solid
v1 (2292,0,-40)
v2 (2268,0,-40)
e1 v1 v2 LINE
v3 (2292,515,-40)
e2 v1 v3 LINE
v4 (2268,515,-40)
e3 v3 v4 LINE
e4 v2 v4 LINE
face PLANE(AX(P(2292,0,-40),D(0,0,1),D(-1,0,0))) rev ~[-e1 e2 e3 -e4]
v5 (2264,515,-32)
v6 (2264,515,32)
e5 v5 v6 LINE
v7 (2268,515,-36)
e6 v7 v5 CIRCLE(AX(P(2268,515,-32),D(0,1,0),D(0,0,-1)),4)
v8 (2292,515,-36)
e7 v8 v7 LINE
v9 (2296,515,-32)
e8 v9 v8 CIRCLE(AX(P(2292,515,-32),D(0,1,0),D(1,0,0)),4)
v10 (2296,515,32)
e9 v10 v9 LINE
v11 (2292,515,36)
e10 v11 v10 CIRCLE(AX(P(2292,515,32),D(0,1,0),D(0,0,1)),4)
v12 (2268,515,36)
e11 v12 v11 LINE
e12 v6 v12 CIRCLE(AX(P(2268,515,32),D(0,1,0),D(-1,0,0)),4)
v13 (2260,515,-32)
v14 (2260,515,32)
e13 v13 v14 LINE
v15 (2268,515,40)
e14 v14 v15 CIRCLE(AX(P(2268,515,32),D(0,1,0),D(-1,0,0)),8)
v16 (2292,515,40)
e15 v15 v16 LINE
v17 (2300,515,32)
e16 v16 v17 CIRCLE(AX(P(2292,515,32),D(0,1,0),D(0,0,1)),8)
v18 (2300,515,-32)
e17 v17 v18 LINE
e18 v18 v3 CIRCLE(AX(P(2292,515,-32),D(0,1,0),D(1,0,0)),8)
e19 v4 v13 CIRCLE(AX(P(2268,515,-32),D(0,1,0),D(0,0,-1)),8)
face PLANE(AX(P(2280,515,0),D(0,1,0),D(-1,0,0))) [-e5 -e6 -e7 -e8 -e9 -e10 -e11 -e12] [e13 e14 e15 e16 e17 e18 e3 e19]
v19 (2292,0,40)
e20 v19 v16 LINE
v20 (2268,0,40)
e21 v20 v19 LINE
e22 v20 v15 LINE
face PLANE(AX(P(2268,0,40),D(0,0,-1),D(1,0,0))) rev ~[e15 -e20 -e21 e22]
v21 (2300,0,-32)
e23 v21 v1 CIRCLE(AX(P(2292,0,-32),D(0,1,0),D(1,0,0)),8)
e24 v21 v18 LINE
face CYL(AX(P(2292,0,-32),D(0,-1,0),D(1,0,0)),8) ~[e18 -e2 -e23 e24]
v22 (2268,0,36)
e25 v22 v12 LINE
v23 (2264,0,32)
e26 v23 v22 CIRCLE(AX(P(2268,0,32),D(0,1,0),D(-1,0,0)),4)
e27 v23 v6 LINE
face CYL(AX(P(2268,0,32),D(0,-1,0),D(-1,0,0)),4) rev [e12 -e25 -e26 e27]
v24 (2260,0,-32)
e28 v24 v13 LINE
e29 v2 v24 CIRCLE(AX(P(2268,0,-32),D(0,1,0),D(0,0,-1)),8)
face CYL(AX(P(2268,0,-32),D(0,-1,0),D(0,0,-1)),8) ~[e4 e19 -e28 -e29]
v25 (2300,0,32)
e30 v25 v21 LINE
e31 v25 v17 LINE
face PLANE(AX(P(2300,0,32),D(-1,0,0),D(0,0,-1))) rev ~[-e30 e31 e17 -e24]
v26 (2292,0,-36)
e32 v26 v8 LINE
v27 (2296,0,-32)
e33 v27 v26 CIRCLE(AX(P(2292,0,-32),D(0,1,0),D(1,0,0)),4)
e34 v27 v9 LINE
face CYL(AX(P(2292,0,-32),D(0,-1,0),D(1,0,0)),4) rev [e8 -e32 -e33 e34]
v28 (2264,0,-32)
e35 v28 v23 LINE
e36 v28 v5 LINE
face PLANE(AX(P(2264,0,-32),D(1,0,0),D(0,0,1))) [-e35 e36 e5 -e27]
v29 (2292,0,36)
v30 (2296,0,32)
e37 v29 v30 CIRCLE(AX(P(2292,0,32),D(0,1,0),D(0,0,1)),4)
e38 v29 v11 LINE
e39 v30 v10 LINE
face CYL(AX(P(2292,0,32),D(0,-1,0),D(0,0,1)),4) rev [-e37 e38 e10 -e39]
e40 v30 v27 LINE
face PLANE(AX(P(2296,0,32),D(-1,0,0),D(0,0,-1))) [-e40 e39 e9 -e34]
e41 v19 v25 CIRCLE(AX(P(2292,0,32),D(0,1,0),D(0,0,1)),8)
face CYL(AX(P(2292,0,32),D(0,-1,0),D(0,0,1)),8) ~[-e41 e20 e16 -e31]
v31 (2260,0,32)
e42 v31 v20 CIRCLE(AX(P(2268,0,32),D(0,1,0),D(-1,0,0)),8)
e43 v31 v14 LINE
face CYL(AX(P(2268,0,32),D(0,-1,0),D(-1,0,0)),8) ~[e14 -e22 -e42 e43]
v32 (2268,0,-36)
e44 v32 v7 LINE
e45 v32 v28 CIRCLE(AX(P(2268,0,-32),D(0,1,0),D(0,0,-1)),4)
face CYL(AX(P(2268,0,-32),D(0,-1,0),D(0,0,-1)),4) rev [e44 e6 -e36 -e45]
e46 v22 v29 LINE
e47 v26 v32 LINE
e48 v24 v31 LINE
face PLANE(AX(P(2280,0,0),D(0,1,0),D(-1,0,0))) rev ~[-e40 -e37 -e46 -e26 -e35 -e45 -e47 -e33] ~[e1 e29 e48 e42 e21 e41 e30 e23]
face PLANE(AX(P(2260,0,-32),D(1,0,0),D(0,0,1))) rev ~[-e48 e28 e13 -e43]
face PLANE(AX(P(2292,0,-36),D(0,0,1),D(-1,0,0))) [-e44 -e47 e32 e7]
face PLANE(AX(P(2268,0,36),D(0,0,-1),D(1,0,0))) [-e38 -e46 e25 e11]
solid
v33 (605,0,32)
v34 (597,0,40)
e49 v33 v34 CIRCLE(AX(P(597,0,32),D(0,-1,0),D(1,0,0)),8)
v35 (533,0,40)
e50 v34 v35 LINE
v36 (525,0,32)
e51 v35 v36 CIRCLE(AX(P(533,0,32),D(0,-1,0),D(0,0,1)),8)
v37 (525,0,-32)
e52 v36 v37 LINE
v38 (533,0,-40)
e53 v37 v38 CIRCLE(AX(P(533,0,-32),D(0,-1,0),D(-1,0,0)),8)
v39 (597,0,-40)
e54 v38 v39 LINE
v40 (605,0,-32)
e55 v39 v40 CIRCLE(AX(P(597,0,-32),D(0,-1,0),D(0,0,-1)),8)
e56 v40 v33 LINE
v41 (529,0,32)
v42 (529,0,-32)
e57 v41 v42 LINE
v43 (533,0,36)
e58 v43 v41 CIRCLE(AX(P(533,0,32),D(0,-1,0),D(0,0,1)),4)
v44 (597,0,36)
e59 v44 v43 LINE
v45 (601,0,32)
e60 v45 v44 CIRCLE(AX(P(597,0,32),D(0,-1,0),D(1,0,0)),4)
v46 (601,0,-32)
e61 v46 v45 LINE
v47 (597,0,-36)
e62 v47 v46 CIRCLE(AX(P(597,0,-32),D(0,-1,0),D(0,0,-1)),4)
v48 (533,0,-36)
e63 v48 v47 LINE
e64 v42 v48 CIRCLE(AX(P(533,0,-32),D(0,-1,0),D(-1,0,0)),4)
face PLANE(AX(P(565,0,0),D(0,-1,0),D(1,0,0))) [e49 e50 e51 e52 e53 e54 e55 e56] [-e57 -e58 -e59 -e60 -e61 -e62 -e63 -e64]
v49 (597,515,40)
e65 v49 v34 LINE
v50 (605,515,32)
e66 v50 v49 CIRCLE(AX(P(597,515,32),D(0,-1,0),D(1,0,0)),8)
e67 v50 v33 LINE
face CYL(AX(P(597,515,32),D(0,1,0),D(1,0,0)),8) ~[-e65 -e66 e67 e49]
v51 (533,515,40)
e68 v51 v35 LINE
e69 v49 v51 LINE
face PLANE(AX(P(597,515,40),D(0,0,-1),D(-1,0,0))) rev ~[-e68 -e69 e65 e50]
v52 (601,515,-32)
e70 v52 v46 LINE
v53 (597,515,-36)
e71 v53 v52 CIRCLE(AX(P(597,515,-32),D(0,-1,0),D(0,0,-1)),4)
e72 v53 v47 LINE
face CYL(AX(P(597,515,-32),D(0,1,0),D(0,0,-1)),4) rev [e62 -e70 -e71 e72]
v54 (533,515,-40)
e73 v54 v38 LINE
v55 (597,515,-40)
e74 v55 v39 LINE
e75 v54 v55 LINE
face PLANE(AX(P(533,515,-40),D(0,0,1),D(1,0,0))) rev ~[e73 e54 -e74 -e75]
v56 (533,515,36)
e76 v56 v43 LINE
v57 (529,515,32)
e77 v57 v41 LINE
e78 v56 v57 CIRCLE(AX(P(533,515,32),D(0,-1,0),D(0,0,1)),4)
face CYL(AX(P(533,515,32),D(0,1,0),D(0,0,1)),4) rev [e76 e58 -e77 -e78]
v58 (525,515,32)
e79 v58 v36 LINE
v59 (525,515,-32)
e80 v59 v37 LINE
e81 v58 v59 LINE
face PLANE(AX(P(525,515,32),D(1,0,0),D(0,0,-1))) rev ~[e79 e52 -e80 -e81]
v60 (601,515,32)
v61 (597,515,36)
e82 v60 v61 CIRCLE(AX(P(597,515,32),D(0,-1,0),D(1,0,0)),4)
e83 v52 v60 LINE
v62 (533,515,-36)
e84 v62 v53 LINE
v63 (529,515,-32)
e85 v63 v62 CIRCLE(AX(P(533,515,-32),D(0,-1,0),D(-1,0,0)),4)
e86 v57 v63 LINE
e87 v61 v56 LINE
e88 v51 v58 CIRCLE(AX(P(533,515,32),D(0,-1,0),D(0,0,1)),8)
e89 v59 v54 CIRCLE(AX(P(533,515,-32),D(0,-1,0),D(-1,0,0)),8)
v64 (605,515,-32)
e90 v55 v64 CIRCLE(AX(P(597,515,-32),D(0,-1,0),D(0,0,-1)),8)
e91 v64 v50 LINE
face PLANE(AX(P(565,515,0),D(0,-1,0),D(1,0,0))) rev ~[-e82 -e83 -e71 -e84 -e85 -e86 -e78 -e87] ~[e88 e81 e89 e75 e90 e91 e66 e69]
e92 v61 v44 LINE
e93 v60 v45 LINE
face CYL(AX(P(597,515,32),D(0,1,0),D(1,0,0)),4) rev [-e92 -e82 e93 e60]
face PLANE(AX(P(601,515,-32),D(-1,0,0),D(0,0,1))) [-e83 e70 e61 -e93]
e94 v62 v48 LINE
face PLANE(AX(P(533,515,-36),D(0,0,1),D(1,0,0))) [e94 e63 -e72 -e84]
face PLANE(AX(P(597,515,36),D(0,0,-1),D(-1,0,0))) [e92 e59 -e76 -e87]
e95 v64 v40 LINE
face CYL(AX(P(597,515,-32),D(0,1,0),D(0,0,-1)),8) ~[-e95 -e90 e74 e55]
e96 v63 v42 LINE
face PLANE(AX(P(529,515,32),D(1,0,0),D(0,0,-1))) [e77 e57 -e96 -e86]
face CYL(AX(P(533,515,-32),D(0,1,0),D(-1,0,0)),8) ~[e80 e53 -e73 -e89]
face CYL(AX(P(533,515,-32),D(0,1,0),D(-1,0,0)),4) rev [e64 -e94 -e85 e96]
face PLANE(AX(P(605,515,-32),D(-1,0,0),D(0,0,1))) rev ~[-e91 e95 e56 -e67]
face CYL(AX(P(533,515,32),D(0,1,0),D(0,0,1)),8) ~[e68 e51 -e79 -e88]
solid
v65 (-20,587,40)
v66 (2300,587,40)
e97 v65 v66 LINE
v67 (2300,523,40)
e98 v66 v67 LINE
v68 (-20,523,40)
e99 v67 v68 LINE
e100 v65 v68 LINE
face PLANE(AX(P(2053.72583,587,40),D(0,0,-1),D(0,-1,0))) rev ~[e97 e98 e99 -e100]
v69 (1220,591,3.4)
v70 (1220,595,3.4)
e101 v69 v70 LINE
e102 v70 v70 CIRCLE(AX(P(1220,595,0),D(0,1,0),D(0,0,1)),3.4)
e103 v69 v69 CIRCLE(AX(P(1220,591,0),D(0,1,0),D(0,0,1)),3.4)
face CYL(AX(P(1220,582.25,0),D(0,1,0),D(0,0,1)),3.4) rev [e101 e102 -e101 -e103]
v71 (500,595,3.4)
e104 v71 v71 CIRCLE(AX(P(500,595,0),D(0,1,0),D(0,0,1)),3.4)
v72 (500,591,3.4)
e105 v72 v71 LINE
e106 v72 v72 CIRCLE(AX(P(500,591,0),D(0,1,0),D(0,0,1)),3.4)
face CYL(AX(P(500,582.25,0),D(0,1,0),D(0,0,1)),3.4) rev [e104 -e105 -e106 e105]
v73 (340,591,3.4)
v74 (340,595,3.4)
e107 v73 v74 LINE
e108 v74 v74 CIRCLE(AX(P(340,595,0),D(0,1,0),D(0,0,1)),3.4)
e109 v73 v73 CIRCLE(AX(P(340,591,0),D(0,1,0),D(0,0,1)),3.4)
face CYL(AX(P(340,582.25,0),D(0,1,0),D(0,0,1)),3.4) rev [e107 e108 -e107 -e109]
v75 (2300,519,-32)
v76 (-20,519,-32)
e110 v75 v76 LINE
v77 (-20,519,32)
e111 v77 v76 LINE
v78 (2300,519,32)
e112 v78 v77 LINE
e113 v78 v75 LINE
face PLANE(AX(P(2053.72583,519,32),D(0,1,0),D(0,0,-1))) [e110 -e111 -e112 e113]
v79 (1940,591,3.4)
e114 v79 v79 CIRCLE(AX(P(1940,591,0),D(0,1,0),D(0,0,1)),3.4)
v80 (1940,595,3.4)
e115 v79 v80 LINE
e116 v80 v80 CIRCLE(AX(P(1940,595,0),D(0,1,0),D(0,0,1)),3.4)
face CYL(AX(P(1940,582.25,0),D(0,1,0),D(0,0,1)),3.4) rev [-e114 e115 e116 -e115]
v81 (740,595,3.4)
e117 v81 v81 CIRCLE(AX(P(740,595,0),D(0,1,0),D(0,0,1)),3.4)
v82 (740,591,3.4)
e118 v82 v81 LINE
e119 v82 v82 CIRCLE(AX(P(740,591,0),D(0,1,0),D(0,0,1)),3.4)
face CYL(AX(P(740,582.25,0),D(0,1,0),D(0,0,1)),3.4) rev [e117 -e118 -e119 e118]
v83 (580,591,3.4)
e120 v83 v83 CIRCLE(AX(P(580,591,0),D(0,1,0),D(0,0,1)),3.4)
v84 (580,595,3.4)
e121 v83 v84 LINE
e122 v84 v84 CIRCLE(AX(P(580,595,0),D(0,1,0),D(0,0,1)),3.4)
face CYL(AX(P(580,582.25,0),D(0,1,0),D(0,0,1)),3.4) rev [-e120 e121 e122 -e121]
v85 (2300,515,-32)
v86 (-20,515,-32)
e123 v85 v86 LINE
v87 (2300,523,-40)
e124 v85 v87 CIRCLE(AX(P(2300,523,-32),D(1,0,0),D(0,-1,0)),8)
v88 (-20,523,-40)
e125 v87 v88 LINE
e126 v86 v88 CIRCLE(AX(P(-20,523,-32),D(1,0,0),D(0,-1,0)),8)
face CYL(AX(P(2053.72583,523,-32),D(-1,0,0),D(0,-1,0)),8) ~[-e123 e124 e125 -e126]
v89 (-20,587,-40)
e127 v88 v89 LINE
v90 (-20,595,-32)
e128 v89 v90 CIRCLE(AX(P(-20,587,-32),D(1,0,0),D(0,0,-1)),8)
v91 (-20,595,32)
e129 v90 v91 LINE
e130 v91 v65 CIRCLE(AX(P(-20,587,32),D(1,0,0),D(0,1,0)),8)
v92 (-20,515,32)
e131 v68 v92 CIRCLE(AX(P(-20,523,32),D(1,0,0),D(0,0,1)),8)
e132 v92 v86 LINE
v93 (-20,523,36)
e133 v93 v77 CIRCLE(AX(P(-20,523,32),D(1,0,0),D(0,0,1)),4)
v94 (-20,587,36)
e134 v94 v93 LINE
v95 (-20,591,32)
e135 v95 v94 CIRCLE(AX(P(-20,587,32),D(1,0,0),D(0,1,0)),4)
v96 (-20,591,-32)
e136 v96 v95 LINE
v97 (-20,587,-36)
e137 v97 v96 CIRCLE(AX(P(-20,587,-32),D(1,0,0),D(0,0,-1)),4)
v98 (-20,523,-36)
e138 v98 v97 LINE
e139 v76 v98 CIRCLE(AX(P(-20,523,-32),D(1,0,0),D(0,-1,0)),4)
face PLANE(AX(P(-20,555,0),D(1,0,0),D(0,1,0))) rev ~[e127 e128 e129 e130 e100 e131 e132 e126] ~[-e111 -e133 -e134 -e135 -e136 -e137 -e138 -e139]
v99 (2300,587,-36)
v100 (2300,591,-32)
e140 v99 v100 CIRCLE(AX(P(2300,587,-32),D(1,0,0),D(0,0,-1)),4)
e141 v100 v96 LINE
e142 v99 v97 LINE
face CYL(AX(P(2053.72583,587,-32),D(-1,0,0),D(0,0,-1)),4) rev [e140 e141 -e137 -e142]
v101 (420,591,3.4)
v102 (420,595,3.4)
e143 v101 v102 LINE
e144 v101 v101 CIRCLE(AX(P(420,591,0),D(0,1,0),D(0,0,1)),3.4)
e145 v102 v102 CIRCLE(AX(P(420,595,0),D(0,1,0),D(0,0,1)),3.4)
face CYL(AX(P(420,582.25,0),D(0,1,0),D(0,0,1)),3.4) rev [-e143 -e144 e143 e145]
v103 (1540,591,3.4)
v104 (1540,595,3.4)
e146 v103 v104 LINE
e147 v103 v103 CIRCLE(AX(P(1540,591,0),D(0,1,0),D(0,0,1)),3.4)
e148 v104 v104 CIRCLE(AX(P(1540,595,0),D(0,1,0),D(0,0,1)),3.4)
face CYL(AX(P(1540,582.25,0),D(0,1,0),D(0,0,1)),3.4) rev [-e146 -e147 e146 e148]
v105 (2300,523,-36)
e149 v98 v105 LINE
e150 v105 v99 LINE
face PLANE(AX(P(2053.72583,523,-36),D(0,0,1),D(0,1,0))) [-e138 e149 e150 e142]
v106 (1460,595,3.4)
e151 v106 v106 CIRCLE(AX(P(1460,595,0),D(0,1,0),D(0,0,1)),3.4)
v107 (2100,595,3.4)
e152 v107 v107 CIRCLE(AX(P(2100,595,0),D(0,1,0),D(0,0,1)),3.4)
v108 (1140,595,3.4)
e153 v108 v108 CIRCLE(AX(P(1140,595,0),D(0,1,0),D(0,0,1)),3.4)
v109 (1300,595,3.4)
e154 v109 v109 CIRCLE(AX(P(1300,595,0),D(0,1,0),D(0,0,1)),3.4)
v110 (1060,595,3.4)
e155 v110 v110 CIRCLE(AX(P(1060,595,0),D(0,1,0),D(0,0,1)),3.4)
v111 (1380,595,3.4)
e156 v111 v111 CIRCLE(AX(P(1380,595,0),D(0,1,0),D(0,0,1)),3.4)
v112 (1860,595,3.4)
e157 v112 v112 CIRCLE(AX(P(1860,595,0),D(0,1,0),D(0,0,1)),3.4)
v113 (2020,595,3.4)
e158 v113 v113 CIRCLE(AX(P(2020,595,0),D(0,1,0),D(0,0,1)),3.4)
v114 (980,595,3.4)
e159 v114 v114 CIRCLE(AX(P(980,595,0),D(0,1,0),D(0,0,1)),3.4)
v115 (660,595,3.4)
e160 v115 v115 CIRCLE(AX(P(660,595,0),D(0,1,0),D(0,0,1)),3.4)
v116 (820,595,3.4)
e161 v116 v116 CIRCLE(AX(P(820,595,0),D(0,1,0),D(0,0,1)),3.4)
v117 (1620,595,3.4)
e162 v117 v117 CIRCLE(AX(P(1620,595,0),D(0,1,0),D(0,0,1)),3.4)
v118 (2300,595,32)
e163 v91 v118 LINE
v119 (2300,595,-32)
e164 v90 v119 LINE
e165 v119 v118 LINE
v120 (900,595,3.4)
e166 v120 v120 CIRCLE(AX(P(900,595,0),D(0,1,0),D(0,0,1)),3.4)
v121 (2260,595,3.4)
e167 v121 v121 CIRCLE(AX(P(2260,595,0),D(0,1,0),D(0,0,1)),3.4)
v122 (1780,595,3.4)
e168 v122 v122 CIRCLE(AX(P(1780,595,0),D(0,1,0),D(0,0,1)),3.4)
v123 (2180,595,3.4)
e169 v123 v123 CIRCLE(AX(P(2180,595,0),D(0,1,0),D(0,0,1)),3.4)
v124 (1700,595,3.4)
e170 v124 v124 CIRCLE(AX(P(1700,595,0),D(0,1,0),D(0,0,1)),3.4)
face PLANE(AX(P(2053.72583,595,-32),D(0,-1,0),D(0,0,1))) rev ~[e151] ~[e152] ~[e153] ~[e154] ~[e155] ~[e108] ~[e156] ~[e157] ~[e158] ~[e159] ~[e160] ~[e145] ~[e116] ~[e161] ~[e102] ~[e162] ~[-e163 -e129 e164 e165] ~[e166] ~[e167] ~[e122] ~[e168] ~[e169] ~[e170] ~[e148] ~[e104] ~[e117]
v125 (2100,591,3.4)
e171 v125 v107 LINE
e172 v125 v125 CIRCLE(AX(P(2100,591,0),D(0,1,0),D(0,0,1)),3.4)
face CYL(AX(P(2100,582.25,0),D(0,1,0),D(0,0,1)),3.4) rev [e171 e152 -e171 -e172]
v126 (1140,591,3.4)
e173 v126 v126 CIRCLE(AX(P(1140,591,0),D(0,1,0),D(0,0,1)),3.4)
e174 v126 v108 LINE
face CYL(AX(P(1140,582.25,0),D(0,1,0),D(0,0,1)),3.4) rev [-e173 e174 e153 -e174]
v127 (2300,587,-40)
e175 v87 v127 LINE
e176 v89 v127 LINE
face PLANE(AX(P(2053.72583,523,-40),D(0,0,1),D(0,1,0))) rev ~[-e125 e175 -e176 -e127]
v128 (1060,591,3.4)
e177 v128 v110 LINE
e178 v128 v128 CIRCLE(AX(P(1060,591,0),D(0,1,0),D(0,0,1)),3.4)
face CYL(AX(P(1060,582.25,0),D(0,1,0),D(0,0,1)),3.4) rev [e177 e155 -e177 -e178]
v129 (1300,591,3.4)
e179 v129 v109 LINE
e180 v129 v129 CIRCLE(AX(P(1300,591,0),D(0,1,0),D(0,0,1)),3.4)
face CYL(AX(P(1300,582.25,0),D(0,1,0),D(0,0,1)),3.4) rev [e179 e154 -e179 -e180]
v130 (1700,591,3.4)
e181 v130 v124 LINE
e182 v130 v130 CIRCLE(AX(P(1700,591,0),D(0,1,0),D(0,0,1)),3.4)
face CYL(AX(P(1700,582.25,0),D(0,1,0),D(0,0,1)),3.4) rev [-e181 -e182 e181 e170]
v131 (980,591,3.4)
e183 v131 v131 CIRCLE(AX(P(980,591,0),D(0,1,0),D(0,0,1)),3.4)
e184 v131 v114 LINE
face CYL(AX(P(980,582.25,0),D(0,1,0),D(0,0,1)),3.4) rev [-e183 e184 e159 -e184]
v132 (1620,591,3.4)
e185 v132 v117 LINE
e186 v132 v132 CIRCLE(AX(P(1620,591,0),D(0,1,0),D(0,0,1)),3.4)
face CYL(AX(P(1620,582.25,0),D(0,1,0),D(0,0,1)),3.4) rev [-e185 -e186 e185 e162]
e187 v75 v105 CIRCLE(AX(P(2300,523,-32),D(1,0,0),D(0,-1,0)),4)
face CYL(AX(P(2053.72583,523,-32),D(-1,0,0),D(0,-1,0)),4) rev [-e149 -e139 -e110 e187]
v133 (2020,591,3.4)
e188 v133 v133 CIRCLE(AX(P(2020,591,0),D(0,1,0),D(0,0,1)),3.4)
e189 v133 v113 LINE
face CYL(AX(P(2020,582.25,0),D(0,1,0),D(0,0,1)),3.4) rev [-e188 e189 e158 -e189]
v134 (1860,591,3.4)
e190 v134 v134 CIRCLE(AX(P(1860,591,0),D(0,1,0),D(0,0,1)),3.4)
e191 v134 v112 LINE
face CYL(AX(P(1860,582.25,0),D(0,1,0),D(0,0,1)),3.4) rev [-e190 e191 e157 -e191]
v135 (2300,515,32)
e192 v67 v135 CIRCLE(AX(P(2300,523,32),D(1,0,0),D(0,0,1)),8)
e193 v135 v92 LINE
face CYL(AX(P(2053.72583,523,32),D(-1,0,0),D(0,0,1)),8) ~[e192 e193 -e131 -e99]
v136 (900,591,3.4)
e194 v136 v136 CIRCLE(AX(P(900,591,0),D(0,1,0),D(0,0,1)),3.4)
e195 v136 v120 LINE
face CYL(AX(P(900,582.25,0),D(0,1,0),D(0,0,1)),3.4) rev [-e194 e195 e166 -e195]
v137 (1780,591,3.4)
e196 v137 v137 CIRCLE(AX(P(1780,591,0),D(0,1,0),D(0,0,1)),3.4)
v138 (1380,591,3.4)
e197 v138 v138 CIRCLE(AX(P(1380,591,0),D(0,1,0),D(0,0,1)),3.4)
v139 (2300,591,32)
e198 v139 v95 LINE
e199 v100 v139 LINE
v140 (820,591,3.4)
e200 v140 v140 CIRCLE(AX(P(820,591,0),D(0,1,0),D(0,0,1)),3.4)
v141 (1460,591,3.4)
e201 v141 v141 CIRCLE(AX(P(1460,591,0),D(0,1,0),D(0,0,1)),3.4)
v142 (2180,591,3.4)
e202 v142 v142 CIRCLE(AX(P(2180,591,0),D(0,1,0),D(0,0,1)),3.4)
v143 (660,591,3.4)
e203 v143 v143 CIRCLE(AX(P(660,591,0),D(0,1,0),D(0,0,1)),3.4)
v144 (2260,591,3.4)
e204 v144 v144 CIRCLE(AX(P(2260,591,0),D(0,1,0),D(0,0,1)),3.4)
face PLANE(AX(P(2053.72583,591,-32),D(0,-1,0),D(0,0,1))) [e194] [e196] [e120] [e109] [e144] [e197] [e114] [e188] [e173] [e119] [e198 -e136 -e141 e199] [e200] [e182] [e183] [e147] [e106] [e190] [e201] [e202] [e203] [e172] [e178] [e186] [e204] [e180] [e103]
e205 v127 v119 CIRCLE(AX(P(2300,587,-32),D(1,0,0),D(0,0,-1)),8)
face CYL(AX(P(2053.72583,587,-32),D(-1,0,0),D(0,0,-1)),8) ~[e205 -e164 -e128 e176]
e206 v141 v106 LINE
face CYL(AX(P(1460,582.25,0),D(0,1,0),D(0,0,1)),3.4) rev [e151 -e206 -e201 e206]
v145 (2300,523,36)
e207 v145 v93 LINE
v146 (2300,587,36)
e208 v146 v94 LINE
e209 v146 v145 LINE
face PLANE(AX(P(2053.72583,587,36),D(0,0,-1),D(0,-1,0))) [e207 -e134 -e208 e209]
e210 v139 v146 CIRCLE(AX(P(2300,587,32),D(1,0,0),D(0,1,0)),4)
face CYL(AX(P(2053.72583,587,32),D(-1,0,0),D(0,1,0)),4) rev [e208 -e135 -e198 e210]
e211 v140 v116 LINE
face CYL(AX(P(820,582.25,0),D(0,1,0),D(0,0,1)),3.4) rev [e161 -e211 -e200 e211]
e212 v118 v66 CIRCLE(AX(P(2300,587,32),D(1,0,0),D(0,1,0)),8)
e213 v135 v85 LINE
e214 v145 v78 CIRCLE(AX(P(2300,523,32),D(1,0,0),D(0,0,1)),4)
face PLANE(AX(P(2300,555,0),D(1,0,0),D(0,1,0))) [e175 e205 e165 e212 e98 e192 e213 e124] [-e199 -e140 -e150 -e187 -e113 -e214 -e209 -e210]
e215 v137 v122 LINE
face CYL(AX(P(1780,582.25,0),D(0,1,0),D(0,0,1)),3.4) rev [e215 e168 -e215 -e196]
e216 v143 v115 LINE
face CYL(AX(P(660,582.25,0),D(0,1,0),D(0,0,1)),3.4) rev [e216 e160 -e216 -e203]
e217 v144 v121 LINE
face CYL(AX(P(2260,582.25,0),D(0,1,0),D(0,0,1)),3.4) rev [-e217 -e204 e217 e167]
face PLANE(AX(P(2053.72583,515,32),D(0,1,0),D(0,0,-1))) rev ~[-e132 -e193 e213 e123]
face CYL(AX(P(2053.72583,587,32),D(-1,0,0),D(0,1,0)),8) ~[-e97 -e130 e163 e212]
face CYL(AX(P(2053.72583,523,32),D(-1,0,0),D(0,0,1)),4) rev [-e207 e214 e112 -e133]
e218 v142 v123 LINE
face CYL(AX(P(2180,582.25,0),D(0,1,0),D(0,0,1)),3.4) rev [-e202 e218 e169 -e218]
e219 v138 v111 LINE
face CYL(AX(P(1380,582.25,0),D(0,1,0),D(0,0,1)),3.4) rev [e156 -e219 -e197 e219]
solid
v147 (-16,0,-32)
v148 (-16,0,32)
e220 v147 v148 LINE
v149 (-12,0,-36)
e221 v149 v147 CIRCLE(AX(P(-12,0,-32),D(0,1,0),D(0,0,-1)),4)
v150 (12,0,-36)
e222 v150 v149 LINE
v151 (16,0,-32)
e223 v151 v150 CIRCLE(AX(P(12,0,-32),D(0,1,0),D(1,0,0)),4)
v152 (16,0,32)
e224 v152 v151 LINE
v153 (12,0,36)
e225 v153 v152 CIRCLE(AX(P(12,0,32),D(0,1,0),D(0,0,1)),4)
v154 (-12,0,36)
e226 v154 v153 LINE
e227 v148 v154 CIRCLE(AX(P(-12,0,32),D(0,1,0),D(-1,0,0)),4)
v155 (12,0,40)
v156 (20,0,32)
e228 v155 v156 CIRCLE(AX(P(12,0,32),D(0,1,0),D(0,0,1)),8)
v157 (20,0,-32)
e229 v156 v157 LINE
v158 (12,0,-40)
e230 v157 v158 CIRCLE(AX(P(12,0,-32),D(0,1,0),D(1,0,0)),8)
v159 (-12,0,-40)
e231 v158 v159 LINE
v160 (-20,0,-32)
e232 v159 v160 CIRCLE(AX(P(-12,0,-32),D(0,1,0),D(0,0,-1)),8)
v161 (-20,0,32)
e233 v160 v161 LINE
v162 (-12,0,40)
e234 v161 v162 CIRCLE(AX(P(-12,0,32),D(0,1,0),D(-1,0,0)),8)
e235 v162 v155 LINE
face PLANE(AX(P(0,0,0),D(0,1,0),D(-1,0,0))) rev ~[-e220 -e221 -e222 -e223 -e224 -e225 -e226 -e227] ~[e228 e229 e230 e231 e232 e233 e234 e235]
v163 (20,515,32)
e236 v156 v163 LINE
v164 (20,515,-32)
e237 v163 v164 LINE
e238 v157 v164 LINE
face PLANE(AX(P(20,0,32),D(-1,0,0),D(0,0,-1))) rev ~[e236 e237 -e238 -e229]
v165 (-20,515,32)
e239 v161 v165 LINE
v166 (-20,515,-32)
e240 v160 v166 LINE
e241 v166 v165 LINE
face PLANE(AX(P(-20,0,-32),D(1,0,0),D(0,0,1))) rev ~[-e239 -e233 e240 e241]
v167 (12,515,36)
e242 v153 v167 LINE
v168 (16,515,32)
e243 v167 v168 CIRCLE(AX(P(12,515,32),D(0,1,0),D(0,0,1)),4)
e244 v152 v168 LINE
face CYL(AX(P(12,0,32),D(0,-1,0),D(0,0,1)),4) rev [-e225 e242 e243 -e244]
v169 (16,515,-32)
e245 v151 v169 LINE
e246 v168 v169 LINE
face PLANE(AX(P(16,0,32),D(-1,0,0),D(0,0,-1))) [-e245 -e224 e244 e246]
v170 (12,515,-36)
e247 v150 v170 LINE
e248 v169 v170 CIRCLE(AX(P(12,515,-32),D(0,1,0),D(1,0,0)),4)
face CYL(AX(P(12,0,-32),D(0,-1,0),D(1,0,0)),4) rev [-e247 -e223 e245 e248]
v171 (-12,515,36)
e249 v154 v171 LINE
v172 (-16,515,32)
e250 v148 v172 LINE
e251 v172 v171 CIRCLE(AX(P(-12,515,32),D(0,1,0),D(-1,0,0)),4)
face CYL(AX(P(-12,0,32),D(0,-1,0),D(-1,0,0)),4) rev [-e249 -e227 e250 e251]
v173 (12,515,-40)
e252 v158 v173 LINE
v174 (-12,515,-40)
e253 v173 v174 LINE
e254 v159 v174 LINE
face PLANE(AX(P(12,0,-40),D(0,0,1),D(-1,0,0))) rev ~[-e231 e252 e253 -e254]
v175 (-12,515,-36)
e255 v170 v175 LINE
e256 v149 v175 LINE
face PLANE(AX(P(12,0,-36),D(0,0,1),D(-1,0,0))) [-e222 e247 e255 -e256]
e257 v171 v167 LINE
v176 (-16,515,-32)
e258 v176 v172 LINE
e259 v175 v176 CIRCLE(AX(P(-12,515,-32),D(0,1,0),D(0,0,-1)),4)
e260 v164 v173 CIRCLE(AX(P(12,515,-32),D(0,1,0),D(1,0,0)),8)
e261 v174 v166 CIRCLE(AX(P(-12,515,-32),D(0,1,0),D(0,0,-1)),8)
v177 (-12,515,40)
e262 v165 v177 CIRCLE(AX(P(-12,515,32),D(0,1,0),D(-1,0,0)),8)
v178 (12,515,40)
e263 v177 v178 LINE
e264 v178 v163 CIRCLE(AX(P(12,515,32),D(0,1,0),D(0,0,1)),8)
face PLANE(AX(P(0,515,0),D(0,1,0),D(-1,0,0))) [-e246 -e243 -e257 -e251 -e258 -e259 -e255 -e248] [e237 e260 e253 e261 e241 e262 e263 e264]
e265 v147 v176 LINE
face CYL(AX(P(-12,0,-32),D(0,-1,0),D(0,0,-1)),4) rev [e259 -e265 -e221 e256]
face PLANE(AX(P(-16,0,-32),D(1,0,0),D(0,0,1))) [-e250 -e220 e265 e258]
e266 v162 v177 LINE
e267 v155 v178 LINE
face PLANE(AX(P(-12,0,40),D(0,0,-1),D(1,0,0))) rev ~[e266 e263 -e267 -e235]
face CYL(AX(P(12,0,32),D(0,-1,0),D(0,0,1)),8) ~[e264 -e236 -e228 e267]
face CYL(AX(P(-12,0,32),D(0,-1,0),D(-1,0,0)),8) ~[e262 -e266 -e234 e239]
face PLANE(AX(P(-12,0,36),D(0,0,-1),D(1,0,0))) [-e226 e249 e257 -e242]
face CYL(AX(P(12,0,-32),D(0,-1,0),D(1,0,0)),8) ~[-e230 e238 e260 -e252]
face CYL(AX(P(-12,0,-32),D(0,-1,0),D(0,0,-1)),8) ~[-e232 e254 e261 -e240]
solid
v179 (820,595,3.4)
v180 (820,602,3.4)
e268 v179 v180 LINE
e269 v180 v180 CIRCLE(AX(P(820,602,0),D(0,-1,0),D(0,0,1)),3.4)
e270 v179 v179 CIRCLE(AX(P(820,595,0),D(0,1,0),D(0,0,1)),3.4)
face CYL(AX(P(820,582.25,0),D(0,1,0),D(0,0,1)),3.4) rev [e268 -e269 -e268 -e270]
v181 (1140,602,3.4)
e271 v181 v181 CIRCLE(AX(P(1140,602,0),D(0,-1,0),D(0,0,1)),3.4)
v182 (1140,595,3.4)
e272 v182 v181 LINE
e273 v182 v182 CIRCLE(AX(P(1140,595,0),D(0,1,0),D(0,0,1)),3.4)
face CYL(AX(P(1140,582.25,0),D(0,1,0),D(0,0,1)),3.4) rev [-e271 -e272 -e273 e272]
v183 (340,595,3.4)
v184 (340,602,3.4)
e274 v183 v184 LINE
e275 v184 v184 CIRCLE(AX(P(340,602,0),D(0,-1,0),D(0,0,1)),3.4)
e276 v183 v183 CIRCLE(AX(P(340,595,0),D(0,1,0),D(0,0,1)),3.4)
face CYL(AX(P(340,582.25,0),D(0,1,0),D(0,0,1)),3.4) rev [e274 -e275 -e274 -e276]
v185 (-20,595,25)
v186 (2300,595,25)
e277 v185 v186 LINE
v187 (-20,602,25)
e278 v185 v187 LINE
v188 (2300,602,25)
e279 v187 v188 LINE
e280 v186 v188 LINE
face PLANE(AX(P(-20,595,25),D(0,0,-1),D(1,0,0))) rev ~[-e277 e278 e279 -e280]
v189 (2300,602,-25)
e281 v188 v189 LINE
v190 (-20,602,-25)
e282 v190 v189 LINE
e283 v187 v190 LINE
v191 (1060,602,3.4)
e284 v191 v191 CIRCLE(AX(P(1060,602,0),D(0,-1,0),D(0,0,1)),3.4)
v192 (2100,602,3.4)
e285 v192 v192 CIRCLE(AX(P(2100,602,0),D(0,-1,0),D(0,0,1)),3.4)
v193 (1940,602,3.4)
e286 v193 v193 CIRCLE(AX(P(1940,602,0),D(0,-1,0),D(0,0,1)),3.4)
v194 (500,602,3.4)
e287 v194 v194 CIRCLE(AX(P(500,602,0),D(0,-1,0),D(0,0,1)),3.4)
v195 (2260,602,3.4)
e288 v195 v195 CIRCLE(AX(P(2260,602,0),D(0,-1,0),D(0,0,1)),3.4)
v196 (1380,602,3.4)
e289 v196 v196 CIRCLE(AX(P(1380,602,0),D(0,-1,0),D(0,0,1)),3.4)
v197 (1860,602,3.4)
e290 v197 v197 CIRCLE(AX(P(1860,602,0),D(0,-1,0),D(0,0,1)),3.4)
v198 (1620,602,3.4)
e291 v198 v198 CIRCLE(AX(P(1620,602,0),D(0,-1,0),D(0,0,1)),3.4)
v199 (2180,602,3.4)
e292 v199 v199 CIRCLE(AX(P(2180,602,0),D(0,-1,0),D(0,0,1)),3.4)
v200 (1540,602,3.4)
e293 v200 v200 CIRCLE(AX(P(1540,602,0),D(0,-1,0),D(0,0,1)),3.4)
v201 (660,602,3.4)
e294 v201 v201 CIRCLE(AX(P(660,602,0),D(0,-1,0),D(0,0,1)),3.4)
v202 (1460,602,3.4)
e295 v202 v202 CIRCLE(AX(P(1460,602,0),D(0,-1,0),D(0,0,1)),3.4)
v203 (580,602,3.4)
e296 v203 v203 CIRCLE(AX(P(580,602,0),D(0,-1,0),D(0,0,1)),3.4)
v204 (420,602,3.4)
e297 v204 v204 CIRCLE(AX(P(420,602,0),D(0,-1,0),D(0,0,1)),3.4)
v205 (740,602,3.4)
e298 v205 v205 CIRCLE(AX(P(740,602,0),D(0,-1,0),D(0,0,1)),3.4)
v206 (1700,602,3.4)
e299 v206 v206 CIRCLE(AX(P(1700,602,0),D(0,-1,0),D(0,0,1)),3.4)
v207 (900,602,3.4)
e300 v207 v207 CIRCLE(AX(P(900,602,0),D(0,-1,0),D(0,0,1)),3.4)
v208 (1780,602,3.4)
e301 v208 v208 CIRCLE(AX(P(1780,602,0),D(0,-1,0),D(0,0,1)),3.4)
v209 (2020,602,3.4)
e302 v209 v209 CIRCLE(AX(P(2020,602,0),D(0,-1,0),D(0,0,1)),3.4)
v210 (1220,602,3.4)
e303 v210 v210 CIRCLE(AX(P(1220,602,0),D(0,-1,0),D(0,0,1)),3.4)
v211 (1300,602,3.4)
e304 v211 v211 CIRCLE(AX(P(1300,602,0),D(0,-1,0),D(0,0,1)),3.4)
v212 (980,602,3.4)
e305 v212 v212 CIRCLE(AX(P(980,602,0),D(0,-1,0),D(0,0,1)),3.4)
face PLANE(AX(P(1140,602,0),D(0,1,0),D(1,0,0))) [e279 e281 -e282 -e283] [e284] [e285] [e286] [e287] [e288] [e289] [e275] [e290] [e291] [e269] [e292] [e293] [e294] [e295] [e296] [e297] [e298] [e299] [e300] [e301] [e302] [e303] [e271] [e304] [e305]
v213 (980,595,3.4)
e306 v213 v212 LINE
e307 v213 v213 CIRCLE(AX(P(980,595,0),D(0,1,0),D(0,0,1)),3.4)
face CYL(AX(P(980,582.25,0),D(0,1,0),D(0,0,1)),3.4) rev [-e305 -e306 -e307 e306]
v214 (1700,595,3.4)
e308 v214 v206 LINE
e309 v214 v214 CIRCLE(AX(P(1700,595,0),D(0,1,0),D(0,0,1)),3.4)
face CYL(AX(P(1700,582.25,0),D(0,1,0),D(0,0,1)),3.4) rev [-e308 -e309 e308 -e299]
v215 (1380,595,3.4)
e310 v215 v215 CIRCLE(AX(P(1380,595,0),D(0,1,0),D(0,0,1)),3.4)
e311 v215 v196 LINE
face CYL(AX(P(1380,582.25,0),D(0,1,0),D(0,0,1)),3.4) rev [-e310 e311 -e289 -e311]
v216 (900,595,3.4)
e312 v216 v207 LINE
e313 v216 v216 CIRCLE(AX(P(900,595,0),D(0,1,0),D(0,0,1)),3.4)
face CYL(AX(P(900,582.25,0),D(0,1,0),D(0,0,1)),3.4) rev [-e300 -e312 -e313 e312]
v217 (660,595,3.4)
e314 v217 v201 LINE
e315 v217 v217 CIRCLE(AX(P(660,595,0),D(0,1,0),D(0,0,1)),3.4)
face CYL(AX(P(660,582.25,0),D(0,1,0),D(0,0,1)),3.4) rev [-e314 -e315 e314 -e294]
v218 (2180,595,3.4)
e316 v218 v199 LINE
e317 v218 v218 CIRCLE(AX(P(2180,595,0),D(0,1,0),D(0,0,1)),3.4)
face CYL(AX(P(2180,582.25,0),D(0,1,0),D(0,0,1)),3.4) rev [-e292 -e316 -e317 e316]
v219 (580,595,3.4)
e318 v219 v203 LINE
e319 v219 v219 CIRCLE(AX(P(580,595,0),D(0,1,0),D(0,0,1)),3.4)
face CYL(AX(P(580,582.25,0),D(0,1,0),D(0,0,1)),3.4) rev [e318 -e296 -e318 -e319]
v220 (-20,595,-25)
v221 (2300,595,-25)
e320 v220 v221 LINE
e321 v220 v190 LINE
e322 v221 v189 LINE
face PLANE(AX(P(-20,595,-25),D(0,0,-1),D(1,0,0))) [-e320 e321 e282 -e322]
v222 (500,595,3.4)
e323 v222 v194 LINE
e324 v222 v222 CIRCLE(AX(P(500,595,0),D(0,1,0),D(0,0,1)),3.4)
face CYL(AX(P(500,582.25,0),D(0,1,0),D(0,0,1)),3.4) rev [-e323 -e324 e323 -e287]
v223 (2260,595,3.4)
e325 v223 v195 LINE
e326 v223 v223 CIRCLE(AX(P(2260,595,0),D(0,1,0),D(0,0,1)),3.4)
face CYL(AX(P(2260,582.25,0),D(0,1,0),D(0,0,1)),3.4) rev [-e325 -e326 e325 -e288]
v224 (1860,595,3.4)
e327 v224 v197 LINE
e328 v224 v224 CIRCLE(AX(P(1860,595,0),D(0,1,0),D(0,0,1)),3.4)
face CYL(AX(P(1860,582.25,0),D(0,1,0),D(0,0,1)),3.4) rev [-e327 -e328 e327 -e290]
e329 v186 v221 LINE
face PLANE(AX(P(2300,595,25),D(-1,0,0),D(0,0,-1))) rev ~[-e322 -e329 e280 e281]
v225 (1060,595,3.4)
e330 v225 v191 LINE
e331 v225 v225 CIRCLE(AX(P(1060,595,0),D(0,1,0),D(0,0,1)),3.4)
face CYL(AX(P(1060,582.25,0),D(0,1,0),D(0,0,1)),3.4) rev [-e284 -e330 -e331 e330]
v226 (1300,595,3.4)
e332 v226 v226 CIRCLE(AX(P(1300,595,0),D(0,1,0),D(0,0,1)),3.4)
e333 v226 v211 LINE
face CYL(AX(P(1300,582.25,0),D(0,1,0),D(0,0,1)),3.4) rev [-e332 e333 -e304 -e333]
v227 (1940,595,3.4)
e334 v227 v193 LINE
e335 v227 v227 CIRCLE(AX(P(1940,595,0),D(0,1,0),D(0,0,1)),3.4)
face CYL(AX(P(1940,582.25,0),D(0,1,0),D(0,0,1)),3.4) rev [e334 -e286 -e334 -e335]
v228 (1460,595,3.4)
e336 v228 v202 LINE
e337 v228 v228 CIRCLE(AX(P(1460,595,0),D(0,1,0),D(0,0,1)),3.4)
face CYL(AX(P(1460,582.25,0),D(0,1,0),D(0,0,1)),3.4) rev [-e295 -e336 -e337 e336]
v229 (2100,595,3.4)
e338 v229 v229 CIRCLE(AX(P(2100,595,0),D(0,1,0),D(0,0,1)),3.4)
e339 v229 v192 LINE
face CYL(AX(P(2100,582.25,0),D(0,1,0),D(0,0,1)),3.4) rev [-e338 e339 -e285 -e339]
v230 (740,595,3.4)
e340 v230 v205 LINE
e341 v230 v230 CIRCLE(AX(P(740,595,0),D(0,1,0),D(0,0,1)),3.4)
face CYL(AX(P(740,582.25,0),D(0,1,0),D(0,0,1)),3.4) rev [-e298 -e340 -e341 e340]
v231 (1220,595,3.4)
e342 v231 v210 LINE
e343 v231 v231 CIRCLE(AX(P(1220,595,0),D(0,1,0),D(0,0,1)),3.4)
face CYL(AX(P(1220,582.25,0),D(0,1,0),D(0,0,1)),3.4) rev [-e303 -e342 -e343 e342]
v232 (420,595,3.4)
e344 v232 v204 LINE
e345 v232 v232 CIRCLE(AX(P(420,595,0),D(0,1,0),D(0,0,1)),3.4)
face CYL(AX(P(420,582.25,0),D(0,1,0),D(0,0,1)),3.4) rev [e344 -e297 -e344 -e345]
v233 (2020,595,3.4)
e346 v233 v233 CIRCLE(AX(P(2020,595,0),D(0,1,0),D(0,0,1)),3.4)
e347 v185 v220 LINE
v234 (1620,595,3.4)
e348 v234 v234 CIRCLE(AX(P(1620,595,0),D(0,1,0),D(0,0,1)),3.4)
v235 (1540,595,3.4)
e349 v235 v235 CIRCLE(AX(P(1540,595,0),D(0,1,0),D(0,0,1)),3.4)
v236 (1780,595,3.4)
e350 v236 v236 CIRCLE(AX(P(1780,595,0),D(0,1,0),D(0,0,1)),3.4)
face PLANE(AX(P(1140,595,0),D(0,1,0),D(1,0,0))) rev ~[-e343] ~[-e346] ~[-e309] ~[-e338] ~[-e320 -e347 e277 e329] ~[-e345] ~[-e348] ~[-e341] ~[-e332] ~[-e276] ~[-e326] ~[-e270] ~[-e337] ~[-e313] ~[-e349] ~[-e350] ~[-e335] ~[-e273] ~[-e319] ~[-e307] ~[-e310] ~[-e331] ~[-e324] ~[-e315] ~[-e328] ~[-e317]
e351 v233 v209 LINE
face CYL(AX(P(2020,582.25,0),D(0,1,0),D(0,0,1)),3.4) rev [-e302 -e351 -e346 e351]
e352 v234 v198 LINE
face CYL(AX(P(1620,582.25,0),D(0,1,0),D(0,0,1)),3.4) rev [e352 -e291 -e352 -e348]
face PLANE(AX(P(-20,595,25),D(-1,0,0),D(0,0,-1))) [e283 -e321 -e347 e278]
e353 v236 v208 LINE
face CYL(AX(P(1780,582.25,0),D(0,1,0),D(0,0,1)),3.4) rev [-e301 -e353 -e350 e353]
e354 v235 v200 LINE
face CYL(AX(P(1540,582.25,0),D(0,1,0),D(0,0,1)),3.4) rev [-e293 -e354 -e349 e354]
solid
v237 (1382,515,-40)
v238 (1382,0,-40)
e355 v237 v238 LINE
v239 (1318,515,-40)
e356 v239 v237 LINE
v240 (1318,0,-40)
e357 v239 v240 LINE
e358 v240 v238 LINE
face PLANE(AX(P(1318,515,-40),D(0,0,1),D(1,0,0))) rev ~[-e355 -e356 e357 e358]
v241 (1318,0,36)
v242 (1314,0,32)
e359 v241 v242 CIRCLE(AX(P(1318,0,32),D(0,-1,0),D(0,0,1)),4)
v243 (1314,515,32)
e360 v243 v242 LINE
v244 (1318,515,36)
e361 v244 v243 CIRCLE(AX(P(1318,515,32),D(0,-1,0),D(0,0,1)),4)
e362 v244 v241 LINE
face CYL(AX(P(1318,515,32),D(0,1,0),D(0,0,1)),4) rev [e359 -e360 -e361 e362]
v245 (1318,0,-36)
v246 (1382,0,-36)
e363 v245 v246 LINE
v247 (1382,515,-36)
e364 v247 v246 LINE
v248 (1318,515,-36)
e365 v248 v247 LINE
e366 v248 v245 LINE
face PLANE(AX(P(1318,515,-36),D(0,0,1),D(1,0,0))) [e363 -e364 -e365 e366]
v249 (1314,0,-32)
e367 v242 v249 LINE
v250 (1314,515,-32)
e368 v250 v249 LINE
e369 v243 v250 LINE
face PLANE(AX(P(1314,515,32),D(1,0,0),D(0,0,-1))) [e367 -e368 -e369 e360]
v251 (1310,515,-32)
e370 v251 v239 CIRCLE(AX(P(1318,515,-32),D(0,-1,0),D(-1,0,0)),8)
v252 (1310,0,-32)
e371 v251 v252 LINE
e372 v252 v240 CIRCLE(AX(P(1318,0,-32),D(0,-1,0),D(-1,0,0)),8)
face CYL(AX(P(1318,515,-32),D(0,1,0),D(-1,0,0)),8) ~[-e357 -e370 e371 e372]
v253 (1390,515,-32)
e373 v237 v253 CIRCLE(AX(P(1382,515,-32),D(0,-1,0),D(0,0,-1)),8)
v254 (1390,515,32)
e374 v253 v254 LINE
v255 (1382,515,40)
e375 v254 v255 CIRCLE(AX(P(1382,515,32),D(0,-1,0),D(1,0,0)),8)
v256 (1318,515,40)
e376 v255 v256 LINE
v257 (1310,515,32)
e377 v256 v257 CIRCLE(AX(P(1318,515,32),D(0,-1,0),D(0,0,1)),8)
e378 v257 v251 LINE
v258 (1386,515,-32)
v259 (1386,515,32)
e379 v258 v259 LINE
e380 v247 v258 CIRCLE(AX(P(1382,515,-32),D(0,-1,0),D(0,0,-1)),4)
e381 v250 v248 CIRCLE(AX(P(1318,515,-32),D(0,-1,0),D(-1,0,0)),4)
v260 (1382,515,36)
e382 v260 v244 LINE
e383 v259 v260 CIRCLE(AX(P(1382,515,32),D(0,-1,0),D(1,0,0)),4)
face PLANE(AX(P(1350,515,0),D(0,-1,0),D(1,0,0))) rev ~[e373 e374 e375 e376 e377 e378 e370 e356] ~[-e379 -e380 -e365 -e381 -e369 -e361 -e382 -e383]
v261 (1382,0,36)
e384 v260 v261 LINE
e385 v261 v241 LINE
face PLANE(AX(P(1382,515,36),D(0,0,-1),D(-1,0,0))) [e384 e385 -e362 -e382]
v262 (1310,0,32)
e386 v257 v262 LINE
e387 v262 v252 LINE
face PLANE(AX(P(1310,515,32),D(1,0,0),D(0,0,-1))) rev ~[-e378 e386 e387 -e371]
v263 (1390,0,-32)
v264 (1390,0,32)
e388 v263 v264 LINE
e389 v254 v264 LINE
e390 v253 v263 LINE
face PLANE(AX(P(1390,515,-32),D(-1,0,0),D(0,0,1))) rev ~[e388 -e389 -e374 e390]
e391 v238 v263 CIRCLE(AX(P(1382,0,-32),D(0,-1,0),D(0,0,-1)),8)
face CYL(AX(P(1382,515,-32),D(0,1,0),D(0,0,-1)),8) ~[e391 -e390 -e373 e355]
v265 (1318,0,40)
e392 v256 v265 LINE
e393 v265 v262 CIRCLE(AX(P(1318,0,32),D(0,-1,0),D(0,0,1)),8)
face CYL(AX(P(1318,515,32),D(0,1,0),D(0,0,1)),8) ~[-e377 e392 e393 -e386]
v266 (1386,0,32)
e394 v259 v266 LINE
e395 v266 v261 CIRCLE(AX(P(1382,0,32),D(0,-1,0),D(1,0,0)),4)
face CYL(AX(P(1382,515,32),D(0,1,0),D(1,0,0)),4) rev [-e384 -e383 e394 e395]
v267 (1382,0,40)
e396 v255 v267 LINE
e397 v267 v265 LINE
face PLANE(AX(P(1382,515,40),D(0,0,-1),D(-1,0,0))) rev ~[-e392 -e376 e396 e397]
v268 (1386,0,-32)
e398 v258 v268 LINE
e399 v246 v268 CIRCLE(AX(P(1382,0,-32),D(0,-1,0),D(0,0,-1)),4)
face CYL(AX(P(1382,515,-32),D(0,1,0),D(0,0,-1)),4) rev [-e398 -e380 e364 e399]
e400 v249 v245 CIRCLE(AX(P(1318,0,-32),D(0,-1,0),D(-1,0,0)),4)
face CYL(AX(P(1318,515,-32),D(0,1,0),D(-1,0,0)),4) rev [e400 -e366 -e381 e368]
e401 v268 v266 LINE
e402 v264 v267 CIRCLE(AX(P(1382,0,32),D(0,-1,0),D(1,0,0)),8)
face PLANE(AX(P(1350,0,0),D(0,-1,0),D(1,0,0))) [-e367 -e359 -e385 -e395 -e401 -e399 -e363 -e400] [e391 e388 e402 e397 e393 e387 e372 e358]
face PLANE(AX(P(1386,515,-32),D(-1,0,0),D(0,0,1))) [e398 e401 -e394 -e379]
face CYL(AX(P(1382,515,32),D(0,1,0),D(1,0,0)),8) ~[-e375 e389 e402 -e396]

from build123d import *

# Parameters (mm, degrees)
GB_6728_1986_RECT_HOLLOW_SECTION_080_X_4_DEPTH = 515
GB_6728_1986_RECT_HOLLOW_SECTION_080_2_DEPTH   = 515
GB_6728_1986_SQUARE_HOLLOW_SECTION_080_X_DEPTH = 2280
BODY_START                                     = 226.27416998
BODY_3_RUN_ON_DEPTH                            = 246.27416998
BODY_START_2                                   = 2053.72583002
BODY_3_RUN_ON_2_DEPTH                          = 246.27416998
SKETCH2_W                                      = 2320
SKETCH2_H                                      = 50
BOSS_EXTRUDE1_DEPTH                            = 10
SKETCH4_W                                      = 2320
SKETCH4_H                                      = 50
CUT_EXTRUDE1_DEPTH                             = 3
LPATTERN1_COUNT                                = 25
LPATTERN1_PITCH                                = 80
SQUARE_TUBE_80_X_80_X_4_0_1_DEPTH              = 515
SQUARE_TUBE_80_X_80_X_4_0_1_2_DEPTH            = 515


with BuildPart() as part:
    # Sketch11 → GB/6728-1986 rect hollow section 080 X 40 X 4(1) (new body)
    with BuildSketch(Plane(origin=(0, 0, 0), x_dir=(-1, 0, 0), z_dir=(0, 1, 0))):
        with BuildLine():
            Line((-12, -40), (12, -40))
            ThreePointArc((12, -40), (17.656854249, -37.656854249), (20, -32))
            Line((20, -32), (20, 32))
            ThreePointArc((20, 32), (17.656854249, 37.656854249), (12, 40))
            Line((12, 40), (-12, 40))
            ThreePointArc((-12, 40), (-17.656854249, 37.656854249), (-20, 32))
            Line((-20, 32), (-20, -32))
            ThreePointArc((-20, -32), (-17.656854249, -37.656854249), (-12, -40))
        make_face()
        with BuildLine():
            Line((-12, -36), (12, -36))
            ThreePointArc((12, -36), (14.828427125, -34.828427125), (16, -32))
            Line((16, -32), (16, 32))
            ThreePointArc((16, 32), (14.828427125, 34.828427125), (12, 36))
            Line((12, 36), (-12, 36))
            ThreePointArc((-12, 36), (-14.828427125, 34.828427125), (-16, 32))
            Line((-16, 32), (-16, -32))
            ThreePointArc((-16, -32), (-14.828427125, -34.828427125), (-12, -36))
        make_face(mode=Mode.SUBTRACT)
    extrude(amount=GB_6728_1986_RECT_HOLLOW_SECTION_080_X_4_DEPTH)


with BuildPart() as body_2:
    # Sketch11 on segment 2 (carried to segment 2) → GB_6728-1986 rect hollow section 080 2 (new body)
    with BuildSketch(Plane(origin=(2280, 0, 0), x_dir=(-1, 0, 0), z_dir=(0, 1, 0))):
        with BuildLine():
            Line((-12, -40), (12, -40))
            ThreePointArc((12, -40), (17.656854249, -37.656854249), (20, -32))
            Line((20, -32), (20, 32))
            ThreePointArc((20, 32), (17.656854249, 37.656854249), (12, 40))
            Line((12, 40), (-12, 40))
            ThreePointArc((-12, 40), (-17.656854249, 37.656854249), (-20, 32))
            Line((-20, 32), (-20, -32))
            ThreePointArc((-20, -32), (-17.656854249, -37.656854249), (-12, -40))
        make_face()
        with BuildLine():
            Line((-12, -36), (12, -36))
            ThreePointArc((12, -36), (14.828427125, -34.828427125), (16, -32))
            Line((16, -32), (16, 32))
            ThreePointArc((16, 32), (14.828427125, 34.828427125), (12, 36))
            Line((12, 36), (-12, 36))
            ThreePointArc((-12, 36), (-14.828427125, 34.828427125), (-16, 32))
            Line((-16, 32), (-16, -32))
            ThreePointArc((-16, -32), (-14.828427125, -34.828427125), (-12, -36))
        make_face(mode=Mode.SUBTRACT)
    extrude(amount=GB_6728_1986_RECT_HOLLOW_SECTION_080_2_DEPTH)


with BuildPart() as body_3:
    # Sketch1 → GB/6728-1986 square hollow section 080 X 80 X 4(1) (new body)
    with BuildSketch(Plane(origin=(0, 555, 0), x_dir=(0, 1, 0), z_dir=(1, 0, 0))):
        with BuildLine():
            Line((-32, -40), (32, -40))
            ThreePointArc((32, -40), (37.656854249, -37.656854249), (40, -32))
            Line((40, -32), (40, 32))
            ThreePointArc((40, 32), (37.656854249, 37.656854249), (32, 40))
            Line((32, 40), (-32, 40))
            ThreePointArc((-32, 40), (-37.656854249, 37.656854249), (-40, 32))
            Line((-40, 32), (-40, -32))
            ThreePointArc((-40, -32), (-37.656854249, -37.656854249), (-32, -40))
        make_face()
        with BuildLine():
            Line((-32, -36), (32, -36))
            ThreePointArc((32, -36), (34.828427125, -34.828427125), (36, -32))
            Line((36, -32), (36, 32))
            ThreePointArc((36, 32), (34.828427125, 34.828427125), (32, 36))
            Line((32, 36), (-32, 36))
            ThreePointArc((-32, 36), (-34.828427125, 34.828427125), (-36, 32))
            Line((-36, 32), (-36, -32))
            ThreePointArc((-36, -32), (-34.828427125, -34.828427125), (-32, -36))
        make_face(mode=Mode.SUBTRACT)
    extrude(amount=GB_6728_1986_SQUARE_HOLLOW_SECTION_080_X_DEPTH)

    # body 3 cut square before the run-on
    split(bisect_by=Plane(origin=(226.27416998, 555, 0), x_dir=(0, 1, 0), z_dir=(1, 0, 0)), keep=Keep.TOP)

    # Sketch1 → body 3 run on (add)
    with BuildSketch(Plane(origin=(0, 555, 0), x_dir=(0, 1, 0), z_dir=(1, 0, 0)).offset(BODY_START)):
        with BuildLine():
            Line((-32, -40), (32, -40))
            ThreePointArc((32, -40), (37.656854249, -37.656854249), (40, -32))
            Line((40, -32), (40, 32))
            ThreePointArc((40, 32), (37.656854249, 37.656854249), (32, 40))
            Line((32, 40), (-32, 40))
            ThreePointArc((-32, 40), (-37.656854249, 37.656854249), (-40, 32))
            Line((-40, 32), (-40, -32))
            ThreePointArc((-40, -32), (-37.656854249, -37.656854249), (-32, -40))
        make_face()
        with BuildLine():
            Line((-32, -36), (32, -36))
            ThreePointArc((32, -36), (34.828427125, -34.828427125), (36, -32))
            Line((36, -32), (36, 32))
            ThreePointArc((36, 32), (34.828427125, 34.828427125), (32, 36))
            Line((32, 36), (-32, 36))
            ThreePointArc((-32, 36), (-34.828427125, 34.828427125), (-36, 32))
            Line((-36, 32), (-36, -32))
            ThreePointArc((-36, -32), (-34.828427125, -34.828427125), (-32, -36))
        make_face(mode=Mode.SUBTRACT)
    extrude(amount=-BODY_3_RUN_ON_DEPTH)

    # body 3 cut square before the run-on
    split(bisect_by=Plane(origin=(2053.72583002, 555, 0), x_dir=(0, -1, 0), z_dir=(-1, 0, 0)), keep=Keep.TOP)

    # Sketch1 → body 3 run on 2 (add)
    with BuildSketch(Plane(origin=(0, 555, 0), x_dir=(0, 1, 0), z_dir=(1, 0, 0)).offset(BODY_START_2)):
        with BuildLine():
            Line((-32, -40), (32, -40))
            ThreePointArc((32, -40), (37.656854249, -37.656854249), (40, -32))
            Line((40, -32), (40, 32))
            ThreePointArc((40, 32), (37.656854249, 37.656854249), (32, 40))
            Line((32, 40), (-32, 40))
            ThreePointArc((-32, 40), (-37.656854249, 37.656854249), (-40, 32))
            Line((-40, 32), (-40, -32))
            ThreePointArc((-40, -32), (-37.656854249, -37.656854249), (-32, -40))
        make_face()
        with BuildLine():
            Line((-32, -36), (32, -36))
            ThreePointArc((32, -36), (34.828427125, -34.828427125), (36, -32))
            Line((36, -32), (36, 32))
            ThreePointArc((36, 32), (34.828427125, 34.828427125), (32, 36))
            Line((32, 36), (-32, 36))
            ThreePointArc((-32, 36), (-34.828427125, 34.828427125), (-36, 32))
            Line((-36, 32), (-36, -32))
            ThreePointArc((-36, -32), (-34.828427125, -34.828427125), (-32, -36))
        make_face(mode=Mode.SUBTRACT)
    extrude(amount=BODY_3_RUN_ON_2_DEPTH)


with BuildPart() as body_4:
    # Sketch2 → Boss-Extrude1 (new body)
    with BuildSketch(Plane(origin=(0, 595, 0), x_dir=(1, 0, 0), z_dir=(0, 1, 0))):
        with Locations((1140, 0)):
            Rectangle(SKETCH2_W, SKETCH2_H)
    extrude(amount=BOSS_EXTRUDE1_DEPTH)

    # Sketch4 → Cut-Extrude1 (cut)
    with BuildSketch(Plane(origin=(0, 605, 0), x_dir=(1, 0, 0), z_dir=(0, 1, 0))):
        with Locations((1140, 0)):
            Rectangle(SKETCH4_W, SKETCH4_H)
    extrude(amount=-CUT_EXTRUDE1_DEPTH, mode=Mode.SUBTRACT)


with BuildPart() as m8_tapped_hole1_tool:
    # Sketch6 → M8 Tapped Hole1 (revolve)
    with BuildSketch(Plane(origin=(2260, 602, 0), x_dir=(0, 0, 1), z_dir=(1, 0, 0))):
        Polygon((0, 0), (0, 21.792926105), (3.4, 19.75), (3.4, 0), align=None)
    m8_tapped_hole1 = revolve(axis=Axis((2260, 608.35, 0), (0, -1, 0)))


with BuildPart() as body_3_1:
    add(body_3.part)

    # M8 Tapped Hole1: cut by m8_tapped_hole1_tool
    add(m8_tapped_hole1_tool.part, mode=Mode.SUBTRACT)


with BuildPart() as body_4_1:
    add(body_4.part)

    # M8 Tapped Hole1: cut by m8_tapped_hole1_tool
    add(m8_tapped_hole1_tool.part, mode=Mode.SUBTRACT)


with BuildPart() as lpattern1_tool:
    # LPattern1: M8 Tapped Hole1 ×25
    with Locations(*[(-i * LPATTERN1_PITCH, 0, 0) for i in range(1, LPATTERN1_COUNT)]):
        add(m8_tapped_hole1)


with BuildPart() as body_3_2:
    add(body_3_1.part)

    # LPattern1: cut by lpattern1_tool
    add(lpattern1_tool.part, mode=Mode.SUBTRACT)


with BuildPart() as body_4_2:
    add(body_4_1.part)

    # LPattern1: cut by lpattern1_tool
    add(lpattern1_tool.part, mode=Mode.SUBTRACT)


with BuildPart() as body_5:
    # Sketch12 → Square tube 80 X 80 X 4.0(1) (new body)
    with BuildSketch(Plane(origin=(565, 515, 0), x_dir=(1, 0, 0), z_dir=(0, -1, 0))):
        with BuildLine():
            Line((-32, -40), (32, -40))
            ThreePointArc((32, -40), (37.656854249, -37.656854249), (40, -32))
            Line((40, -32), (40, 32))
            ThreePointArc((40, 32), (37.656854249, 37.656854249), (32, 40))
            Line((32, 40), (-32, 40))
            ThreePointArc((-32, 40), (-37.656854249, 37.656854249), (-40, 32))
            Line((-40, 32), (-40, -32))
            ThreePointArc((-40, -32), (-37.656854249, -37.656854249), (-32, -40))
        make_face()
        with BuildLine():
            Line((-32, -36), (32, -36))
            ThreePointArc((32, -36), (34.828427125, -34.828427125), (36, -32))
            Line((36, -32), (36, 32))
            ThreePointArc((36, 32), (34.828427125, 34.828427125), (32, 36))
            Line((32, 36), (-32, 36))
            ThreePointArc((-32, 36), (-34.828427125, 34.828427125), (-36, 32))
            Line((-36, 32), (-36, -32))
            ThreePointArc((-36, -32), (-34.828427125, -34.828427125), (-32, -36))
        make_face(mode=Mode.SUBTRACT)
    extrude(amount=SQUARE_TUBE_80_X_80_X_4_0_1_DEPTH)


with BuildPart() as body_6:
    # Sketch12 on segment 2 (carried to segment 2) → Square tube 80 X 80 X 4.0_1 2 (new body)
    with BuildSketch(Plane(origin=(1350, 515, 0), x_dir=(1, 0, 0), z_dir=(0, -1, 0))):
        with BuildLine():
            Line((-32, -40), (32, -40))
            ThreePointArc((32, -40), (37.656854249, -37.656854249), (40, -32))
            Line((40, -32), (40, 32))
            ThreePointArc((40, 32), (37.656854249, 37.656854249), (32, 40))
            Line((32, 40), (-32, 40))
            ThreePointArc((-32, 40), (-37.656854249, 37.656854249), (-40, 32))
            Line((-40, 32), (-40, -32))
            ThreePointArc((-40, -32), (-37.656854249, -37.656854249), (-32, -40))
        make_face()
        with BuildLine():
            Line((-32, -36), (32, -36))
            ThreePointArc((32, -36), (34.828427125, -34.828427125), (36, -32))
            Line((36, -32), (36, 32))
            ThreePointArc((36, 32), (34.828427125, 34.828427125), (32, 36))
            Line((32, 36), (-32, 36))
            ThreePointArc((-32, 36), (-34.828427125, 34.828427125), (-36, 32))
            Line((-36, 32), (-36, -32))
            ThreePointArc((-36, -32), (-34.828427125, -34.828427125), (-32, -36))
        make_face(mode=Mode.SUBTRACT)
    extrude(amount=SQUARE_TUBE_80_X_80_X_4_0_1_2_DEPTH)


solid = Compound([part.part, body_2.part, body_3_2.part, body_4_2.part, body_5.part, body_6.part])
